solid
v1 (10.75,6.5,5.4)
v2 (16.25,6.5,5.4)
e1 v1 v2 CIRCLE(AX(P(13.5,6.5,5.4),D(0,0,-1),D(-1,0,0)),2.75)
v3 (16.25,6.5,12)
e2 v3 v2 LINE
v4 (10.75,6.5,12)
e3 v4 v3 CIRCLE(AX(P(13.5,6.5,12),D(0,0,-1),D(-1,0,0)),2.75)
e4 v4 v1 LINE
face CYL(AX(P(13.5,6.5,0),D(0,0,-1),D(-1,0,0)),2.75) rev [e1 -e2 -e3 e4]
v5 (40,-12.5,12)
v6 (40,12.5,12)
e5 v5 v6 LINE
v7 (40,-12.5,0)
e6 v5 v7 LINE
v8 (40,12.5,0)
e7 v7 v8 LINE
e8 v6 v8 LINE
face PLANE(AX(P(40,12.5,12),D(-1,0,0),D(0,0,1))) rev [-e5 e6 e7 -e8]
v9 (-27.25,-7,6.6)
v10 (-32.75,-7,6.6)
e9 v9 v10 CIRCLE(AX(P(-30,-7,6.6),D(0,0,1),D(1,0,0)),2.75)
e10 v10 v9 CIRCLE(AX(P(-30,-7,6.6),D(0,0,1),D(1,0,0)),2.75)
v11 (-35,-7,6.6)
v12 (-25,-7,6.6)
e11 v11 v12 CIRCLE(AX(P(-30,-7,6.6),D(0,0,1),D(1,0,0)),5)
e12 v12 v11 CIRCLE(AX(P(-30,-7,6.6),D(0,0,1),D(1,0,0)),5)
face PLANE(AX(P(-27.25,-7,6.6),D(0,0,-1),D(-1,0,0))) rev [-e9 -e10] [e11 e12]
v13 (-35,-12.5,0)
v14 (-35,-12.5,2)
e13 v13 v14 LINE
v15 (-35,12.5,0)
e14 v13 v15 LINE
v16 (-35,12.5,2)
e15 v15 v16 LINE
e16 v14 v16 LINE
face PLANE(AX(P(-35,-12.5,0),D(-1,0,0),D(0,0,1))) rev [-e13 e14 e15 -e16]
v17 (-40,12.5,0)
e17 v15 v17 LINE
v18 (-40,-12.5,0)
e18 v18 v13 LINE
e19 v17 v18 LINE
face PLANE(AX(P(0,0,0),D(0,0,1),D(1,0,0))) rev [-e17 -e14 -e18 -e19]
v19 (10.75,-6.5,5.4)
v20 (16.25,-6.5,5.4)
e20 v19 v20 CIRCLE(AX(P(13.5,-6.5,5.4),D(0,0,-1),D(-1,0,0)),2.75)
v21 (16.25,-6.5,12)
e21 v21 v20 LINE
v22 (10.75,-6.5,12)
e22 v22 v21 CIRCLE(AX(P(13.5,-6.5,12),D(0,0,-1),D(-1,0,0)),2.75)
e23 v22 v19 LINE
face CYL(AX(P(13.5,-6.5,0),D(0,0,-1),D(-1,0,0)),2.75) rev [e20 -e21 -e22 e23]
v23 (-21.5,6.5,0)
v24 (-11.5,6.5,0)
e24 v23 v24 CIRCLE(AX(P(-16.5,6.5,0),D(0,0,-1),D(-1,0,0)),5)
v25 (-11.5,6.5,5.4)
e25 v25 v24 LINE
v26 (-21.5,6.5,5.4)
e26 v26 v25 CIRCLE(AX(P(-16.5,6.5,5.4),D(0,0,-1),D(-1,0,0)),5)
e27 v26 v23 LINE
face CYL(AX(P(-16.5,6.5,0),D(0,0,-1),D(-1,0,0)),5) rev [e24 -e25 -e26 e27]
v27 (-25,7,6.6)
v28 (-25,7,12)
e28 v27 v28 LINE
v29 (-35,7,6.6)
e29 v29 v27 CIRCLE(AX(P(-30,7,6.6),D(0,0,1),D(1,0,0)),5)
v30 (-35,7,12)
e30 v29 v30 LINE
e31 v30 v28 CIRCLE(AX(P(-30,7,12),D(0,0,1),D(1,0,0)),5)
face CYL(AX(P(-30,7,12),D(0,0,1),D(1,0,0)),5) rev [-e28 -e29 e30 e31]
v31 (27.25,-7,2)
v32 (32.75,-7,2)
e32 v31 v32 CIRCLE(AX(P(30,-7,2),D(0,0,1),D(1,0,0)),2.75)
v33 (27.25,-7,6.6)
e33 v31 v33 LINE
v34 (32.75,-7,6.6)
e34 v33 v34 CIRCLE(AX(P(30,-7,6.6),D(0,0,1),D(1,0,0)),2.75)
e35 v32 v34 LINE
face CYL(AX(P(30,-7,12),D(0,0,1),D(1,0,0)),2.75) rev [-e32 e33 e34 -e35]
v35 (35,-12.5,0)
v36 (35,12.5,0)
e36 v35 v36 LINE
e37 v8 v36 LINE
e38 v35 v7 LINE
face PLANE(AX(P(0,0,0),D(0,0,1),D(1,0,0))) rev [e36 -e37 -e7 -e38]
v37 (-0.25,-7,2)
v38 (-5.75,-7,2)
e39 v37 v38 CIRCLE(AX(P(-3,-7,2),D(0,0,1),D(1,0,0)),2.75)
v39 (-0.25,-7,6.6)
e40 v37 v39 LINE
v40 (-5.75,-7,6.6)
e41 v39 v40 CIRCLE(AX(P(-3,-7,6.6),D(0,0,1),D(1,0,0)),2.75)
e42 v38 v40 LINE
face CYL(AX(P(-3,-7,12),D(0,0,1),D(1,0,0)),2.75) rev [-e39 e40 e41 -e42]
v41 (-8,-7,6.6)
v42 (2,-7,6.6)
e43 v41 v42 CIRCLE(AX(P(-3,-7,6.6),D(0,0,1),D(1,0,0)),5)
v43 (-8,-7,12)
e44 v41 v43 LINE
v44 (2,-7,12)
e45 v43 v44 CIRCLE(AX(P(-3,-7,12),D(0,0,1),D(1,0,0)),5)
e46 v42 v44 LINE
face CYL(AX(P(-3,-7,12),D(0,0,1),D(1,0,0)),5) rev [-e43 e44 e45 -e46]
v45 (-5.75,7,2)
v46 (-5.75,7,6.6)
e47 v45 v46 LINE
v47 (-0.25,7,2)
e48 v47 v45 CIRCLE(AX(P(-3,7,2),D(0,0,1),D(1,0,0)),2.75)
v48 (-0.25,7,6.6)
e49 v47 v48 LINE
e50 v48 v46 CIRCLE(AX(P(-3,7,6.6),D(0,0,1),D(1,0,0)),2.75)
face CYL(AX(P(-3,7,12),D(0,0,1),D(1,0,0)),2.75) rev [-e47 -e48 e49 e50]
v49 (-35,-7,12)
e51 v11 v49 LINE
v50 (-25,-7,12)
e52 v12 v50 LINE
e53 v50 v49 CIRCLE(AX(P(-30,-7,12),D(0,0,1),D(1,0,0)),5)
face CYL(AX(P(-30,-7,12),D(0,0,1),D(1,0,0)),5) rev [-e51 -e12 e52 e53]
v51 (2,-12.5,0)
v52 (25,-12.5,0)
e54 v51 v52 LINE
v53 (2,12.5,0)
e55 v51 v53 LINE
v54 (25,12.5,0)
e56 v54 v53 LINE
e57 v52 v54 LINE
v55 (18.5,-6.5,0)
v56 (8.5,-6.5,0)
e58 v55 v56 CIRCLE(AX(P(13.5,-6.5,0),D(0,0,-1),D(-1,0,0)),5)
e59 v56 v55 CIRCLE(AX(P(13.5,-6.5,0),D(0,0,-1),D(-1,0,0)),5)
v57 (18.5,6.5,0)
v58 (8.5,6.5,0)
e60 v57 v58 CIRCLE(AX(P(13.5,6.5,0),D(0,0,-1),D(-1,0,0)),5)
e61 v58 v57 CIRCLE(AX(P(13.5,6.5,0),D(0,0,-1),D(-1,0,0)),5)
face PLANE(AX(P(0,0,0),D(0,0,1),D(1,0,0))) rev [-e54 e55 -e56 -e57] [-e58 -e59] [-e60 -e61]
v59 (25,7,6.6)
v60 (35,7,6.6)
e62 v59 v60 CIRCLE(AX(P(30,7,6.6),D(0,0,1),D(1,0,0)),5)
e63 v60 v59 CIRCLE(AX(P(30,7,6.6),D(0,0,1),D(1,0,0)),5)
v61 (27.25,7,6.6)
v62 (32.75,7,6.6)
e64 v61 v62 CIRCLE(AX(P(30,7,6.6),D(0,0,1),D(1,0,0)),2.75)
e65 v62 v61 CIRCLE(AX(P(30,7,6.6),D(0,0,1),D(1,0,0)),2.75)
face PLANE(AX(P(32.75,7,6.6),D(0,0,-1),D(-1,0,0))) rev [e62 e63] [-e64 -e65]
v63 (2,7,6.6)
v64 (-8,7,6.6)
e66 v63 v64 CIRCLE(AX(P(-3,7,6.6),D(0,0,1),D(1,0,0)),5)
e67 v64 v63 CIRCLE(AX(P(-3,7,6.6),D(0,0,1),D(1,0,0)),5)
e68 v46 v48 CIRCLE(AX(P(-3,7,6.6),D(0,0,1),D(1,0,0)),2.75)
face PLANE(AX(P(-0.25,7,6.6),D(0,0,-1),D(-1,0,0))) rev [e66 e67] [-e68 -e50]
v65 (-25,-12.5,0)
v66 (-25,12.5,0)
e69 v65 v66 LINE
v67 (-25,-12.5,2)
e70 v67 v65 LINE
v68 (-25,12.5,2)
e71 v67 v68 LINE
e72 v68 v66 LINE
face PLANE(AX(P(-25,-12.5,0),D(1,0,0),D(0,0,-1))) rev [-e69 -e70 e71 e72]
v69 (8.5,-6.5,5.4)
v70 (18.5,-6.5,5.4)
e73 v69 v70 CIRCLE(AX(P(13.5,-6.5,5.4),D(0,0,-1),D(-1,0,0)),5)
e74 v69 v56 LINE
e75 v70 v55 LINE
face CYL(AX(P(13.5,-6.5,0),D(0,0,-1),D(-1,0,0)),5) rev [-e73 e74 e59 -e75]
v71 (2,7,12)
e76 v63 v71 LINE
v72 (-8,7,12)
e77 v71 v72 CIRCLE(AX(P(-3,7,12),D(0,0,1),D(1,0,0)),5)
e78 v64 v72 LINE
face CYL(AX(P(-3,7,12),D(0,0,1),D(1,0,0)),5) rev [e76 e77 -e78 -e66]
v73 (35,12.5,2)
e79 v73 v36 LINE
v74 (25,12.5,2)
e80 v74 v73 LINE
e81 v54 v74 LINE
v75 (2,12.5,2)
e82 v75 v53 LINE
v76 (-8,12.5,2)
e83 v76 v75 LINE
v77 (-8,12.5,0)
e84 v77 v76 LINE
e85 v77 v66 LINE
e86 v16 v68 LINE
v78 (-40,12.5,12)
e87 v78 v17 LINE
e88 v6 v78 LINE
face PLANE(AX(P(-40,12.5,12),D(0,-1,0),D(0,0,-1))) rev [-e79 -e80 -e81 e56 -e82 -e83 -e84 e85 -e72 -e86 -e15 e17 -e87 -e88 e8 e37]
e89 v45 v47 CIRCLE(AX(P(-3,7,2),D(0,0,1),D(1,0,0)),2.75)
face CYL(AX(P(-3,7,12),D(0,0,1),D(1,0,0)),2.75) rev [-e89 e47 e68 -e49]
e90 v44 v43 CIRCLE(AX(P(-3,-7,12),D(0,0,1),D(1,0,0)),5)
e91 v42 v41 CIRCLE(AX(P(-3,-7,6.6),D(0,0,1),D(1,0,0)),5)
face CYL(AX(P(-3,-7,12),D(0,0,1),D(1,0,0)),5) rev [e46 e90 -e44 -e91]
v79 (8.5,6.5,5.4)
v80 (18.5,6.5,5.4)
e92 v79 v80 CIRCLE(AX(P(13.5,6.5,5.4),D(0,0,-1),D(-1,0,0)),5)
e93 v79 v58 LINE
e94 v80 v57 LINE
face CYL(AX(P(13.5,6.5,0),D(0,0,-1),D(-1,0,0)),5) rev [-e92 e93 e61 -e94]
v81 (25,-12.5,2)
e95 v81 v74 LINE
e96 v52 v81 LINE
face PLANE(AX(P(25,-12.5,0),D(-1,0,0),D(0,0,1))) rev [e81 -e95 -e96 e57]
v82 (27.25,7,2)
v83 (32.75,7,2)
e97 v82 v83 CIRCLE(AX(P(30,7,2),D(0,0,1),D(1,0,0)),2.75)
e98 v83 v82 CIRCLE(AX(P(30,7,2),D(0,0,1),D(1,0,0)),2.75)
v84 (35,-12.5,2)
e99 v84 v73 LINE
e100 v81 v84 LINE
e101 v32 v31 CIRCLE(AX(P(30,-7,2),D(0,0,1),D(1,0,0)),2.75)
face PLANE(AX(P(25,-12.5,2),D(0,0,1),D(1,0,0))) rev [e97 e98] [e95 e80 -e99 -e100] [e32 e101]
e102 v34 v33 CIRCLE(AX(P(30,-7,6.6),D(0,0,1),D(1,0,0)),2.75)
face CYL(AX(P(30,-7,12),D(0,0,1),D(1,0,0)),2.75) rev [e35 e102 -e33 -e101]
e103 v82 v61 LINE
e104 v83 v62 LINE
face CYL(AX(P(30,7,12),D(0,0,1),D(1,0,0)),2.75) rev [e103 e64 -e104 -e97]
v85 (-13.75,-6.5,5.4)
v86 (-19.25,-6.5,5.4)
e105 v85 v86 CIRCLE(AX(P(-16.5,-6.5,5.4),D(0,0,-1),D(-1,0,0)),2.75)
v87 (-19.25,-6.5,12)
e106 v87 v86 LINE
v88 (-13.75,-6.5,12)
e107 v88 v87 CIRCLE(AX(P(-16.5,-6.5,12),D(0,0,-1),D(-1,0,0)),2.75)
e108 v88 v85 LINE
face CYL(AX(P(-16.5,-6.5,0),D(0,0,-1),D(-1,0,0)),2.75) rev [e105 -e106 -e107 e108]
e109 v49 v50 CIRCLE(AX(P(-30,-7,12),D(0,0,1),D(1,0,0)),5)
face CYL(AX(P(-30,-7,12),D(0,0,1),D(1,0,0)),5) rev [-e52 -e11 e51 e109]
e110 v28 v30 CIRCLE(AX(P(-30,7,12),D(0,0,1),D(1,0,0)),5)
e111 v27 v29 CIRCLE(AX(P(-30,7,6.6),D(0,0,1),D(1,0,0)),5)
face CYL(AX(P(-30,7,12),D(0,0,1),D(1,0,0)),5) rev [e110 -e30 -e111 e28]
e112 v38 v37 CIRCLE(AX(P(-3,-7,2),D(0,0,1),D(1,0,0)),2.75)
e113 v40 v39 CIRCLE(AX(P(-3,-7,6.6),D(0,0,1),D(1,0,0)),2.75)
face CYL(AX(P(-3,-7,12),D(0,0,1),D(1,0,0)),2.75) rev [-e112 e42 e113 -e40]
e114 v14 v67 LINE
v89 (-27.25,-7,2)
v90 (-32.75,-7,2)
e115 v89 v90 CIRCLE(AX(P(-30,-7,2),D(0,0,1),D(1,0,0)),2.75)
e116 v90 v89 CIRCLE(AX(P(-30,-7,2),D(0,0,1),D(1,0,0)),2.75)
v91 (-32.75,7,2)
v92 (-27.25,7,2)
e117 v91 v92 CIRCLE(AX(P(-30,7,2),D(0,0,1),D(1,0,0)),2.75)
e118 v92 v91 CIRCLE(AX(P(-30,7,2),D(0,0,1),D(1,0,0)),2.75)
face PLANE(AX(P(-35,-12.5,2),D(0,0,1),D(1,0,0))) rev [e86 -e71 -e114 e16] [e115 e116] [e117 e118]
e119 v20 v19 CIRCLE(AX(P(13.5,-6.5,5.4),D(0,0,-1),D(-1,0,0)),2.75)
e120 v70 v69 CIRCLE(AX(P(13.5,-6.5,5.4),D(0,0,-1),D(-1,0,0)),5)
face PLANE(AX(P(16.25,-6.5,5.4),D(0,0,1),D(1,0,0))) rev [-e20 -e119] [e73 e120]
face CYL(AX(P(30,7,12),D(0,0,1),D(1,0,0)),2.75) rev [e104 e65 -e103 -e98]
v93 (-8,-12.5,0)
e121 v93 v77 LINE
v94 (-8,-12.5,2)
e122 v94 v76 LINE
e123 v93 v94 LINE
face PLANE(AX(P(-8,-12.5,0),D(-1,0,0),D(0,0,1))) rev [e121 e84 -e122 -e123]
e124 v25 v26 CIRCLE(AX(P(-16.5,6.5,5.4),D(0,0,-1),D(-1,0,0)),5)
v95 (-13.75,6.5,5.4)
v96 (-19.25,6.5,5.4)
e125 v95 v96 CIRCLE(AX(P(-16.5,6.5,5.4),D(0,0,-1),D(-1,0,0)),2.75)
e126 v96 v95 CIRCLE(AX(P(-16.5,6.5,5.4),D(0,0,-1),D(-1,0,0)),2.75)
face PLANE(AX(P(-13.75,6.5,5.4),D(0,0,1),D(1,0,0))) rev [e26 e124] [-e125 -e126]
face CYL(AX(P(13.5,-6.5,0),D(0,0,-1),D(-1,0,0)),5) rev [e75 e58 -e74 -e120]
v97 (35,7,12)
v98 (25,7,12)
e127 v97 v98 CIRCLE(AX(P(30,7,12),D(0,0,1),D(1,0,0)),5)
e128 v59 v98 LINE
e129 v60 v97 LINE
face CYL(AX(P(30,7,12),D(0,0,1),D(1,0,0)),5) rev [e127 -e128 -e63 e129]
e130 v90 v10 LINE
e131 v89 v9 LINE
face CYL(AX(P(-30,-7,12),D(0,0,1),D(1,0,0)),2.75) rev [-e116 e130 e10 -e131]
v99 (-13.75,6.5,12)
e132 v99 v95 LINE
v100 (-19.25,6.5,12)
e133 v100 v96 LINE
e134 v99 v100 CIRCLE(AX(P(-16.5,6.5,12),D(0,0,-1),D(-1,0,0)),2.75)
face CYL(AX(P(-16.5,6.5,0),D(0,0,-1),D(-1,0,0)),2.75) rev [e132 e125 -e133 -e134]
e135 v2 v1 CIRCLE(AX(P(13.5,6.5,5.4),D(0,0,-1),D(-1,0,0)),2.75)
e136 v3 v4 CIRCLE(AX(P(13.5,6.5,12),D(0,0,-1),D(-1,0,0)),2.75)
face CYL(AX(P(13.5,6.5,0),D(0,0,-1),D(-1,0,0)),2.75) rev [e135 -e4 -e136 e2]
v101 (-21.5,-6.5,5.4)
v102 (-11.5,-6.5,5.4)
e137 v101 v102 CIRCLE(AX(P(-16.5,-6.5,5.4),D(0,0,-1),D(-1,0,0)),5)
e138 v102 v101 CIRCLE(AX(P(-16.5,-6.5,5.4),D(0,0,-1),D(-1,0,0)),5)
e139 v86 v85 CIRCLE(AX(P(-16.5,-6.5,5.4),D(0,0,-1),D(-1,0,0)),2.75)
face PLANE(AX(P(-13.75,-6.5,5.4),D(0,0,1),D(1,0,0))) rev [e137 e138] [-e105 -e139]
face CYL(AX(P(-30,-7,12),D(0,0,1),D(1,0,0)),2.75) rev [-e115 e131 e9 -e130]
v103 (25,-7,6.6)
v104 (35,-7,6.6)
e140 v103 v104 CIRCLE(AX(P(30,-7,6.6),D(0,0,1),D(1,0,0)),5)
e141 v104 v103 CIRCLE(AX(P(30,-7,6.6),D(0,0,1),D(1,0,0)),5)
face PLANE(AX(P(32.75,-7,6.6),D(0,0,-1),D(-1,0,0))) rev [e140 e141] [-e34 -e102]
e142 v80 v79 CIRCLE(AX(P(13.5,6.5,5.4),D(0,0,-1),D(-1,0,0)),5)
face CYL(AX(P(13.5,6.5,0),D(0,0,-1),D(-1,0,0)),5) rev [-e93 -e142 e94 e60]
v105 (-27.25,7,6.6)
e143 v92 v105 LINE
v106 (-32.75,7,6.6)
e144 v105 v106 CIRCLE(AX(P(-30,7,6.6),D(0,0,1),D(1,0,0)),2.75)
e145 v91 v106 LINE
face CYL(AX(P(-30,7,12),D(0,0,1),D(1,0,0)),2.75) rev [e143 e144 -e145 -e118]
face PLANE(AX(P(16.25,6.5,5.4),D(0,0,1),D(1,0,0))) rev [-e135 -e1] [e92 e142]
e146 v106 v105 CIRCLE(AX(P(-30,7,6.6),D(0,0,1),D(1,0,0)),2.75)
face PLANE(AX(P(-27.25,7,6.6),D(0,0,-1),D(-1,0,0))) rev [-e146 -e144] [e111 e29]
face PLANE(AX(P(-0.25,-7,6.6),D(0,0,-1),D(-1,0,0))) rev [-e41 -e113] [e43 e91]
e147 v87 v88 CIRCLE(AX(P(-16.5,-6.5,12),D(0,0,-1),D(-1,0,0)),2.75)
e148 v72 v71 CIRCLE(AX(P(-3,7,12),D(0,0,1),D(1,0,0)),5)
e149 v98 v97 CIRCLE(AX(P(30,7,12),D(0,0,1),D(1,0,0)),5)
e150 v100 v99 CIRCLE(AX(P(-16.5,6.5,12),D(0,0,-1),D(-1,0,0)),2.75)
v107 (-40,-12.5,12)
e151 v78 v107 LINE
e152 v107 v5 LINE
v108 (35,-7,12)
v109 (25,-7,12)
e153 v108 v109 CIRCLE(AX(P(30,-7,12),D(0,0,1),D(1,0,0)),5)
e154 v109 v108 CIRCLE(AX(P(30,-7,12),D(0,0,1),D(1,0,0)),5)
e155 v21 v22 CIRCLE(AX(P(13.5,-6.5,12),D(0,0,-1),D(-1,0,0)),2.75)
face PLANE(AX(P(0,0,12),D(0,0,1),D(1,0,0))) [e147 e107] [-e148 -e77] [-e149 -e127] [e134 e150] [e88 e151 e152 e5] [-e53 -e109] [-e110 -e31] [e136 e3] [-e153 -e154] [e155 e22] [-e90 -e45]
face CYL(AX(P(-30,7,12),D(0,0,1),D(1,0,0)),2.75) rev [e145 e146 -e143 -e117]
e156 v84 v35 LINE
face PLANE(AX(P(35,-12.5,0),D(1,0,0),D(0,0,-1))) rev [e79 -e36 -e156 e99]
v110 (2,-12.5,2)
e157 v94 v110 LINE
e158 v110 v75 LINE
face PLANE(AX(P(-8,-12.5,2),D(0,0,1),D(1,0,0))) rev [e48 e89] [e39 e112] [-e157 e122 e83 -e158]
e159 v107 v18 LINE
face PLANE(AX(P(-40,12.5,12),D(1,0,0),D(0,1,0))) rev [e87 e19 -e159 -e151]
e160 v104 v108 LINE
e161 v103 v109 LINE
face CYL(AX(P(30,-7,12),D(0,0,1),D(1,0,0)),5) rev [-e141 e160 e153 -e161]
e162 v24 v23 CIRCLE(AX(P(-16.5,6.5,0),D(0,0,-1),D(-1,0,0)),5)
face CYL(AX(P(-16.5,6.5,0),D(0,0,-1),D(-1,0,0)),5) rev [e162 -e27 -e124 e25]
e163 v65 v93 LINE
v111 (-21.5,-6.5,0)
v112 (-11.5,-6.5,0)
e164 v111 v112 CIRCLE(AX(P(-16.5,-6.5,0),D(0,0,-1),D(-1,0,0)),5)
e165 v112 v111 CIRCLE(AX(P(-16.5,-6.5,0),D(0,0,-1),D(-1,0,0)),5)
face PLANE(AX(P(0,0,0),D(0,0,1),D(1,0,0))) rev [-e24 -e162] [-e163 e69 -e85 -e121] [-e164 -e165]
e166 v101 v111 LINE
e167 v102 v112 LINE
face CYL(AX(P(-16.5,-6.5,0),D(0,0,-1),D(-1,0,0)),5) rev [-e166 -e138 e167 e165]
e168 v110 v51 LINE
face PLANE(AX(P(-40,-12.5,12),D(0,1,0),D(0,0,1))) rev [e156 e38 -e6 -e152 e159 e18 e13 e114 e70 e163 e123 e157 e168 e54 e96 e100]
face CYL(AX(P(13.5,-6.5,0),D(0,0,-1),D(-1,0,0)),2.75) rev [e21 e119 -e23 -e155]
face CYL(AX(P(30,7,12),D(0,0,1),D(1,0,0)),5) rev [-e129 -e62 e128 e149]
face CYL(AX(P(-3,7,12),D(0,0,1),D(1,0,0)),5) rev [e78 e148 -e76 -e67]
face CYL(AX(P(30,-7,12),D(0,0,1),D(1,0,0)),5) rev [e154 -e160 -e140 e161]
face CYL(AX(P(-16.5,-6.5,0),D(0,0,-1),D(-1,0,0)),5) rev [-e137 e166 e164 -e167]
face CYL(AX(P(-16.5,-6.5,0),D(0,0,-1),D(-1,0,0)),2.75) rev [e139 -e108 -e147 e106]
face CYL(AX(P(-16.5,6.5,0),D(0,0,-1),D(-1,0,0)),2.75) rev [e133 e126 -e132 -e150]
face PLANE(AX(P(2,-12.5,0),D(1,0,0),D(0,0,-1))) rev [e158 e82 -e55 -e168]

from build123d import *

# Parameters (mm, degrees)
SKETCH1_W                                           = 80
SKETCH1_H                                           = 25
BOSS_EXTRUDE1_DEPTH                                 = 12
SKETCH2_W                                           = 10
SKETCH2_H                                           = 2
CUT_EXTRUDE1_DEPTH                                  = 49.672374095
CBORE_FOR_M5_HEX_SOCKET_HEAD_CAP_SCREW1_D           = 5.5
CBORE_FOR_M5_HEX_SOCKET_HEAD_CAP_SCREW1_CBORE_D     = 10
CBORE_FOR_M5_HEX_SOCKET_HEAD_CAP_SCREW1_CBORE_DEPTH = 5.4
CBORE_FOR_M5_HEX_SOCKET_HEAD_CAP_SCREW2_D           = 5.5
CBORE_FOR_M5_HEX_SOCKET_HEAD_CAP_SCREW2_CBORE_D     = 10
CBORE_FOR_M5_HEX_SOCKET_HEAD_CAP_SCREW2_CBORE_DEPTH = 5.4


with BuildPart() as part:
    # Sketch1 → Boss-Extrude1 (new body)
    with BuildSketch(Plane.XY):
        Rectangle(SKETCH1_W, SKETCH1_H)
    extrude(amount=BOSS_EXTRUDE1_DEPTH)

    # Sketch2 → Cut-Extrude1 (cut, through all)
    with BuildSketch(Plane(origin=(0, 12.5, 0), x_dir=(1, 0, 0), z_dir=(0, 1, 0))):
        with Locations((-30, -1)):
            Rectangle(SKETCH2_W, SKETCH2_H)
        with Locations((-3, -1)):
            Rectangle(SKETCH2_W, SKETCH2_H)
        with Locations((30, -1)):
            Rectangle(SKETCH2_W, SKETCH2_H)
    extrude(amount=-CUT_EXTRUDE1_DEPTH, mode=Mode.SUBTRACT)

    # CBORE for M5 Hex Socket Head Cap Screw1 (through all)
    with Locations(Plane.XY.offset(12)):
        with Locations((-30, 7), (-30, -7), (-3, 7), (-3, -7), (30, 7), (30, -7)):
            CounterBoreHole(CBORE_FOR_M5_HEX_SOCKET_HEAD_CAP_SCREW1_D / 2, CBORE_FOR_M5_HEX_SOCKET_HEAD_CAP_SCREW1_CBORE_D / 2, CBORE_FOR_M5_HEX_SOCKET_HEAD_CAP_SCREW1_CBORE_DEPTH)

    # CBORE for M5 Hex Socket Head Cap Screw2 (through all)
    with Locations(Plane(origin=(0, 0, 0), x_dir=(-1, 0, 0), z_dir=(0, 0, -1))):
        with Locations((-13.5, 6.5), (-13.5, -6.5), (16.5, 6.5), (16.5, -6.5)):
            CounterBoreHole(CBORE_FOR_M5_HEX_SOCKET_HEAD_CAP_SCREW2_D / 2, CBORE_FOR_M5_HEX_SOCKET_HEAD_CAP_SCREW2_CBORE_D / 2, CBORE_FOR_M5_HEX_SOCKET_HEAD_CAP_SCREW2_CBORE_DEPTH)


solid = part.part
